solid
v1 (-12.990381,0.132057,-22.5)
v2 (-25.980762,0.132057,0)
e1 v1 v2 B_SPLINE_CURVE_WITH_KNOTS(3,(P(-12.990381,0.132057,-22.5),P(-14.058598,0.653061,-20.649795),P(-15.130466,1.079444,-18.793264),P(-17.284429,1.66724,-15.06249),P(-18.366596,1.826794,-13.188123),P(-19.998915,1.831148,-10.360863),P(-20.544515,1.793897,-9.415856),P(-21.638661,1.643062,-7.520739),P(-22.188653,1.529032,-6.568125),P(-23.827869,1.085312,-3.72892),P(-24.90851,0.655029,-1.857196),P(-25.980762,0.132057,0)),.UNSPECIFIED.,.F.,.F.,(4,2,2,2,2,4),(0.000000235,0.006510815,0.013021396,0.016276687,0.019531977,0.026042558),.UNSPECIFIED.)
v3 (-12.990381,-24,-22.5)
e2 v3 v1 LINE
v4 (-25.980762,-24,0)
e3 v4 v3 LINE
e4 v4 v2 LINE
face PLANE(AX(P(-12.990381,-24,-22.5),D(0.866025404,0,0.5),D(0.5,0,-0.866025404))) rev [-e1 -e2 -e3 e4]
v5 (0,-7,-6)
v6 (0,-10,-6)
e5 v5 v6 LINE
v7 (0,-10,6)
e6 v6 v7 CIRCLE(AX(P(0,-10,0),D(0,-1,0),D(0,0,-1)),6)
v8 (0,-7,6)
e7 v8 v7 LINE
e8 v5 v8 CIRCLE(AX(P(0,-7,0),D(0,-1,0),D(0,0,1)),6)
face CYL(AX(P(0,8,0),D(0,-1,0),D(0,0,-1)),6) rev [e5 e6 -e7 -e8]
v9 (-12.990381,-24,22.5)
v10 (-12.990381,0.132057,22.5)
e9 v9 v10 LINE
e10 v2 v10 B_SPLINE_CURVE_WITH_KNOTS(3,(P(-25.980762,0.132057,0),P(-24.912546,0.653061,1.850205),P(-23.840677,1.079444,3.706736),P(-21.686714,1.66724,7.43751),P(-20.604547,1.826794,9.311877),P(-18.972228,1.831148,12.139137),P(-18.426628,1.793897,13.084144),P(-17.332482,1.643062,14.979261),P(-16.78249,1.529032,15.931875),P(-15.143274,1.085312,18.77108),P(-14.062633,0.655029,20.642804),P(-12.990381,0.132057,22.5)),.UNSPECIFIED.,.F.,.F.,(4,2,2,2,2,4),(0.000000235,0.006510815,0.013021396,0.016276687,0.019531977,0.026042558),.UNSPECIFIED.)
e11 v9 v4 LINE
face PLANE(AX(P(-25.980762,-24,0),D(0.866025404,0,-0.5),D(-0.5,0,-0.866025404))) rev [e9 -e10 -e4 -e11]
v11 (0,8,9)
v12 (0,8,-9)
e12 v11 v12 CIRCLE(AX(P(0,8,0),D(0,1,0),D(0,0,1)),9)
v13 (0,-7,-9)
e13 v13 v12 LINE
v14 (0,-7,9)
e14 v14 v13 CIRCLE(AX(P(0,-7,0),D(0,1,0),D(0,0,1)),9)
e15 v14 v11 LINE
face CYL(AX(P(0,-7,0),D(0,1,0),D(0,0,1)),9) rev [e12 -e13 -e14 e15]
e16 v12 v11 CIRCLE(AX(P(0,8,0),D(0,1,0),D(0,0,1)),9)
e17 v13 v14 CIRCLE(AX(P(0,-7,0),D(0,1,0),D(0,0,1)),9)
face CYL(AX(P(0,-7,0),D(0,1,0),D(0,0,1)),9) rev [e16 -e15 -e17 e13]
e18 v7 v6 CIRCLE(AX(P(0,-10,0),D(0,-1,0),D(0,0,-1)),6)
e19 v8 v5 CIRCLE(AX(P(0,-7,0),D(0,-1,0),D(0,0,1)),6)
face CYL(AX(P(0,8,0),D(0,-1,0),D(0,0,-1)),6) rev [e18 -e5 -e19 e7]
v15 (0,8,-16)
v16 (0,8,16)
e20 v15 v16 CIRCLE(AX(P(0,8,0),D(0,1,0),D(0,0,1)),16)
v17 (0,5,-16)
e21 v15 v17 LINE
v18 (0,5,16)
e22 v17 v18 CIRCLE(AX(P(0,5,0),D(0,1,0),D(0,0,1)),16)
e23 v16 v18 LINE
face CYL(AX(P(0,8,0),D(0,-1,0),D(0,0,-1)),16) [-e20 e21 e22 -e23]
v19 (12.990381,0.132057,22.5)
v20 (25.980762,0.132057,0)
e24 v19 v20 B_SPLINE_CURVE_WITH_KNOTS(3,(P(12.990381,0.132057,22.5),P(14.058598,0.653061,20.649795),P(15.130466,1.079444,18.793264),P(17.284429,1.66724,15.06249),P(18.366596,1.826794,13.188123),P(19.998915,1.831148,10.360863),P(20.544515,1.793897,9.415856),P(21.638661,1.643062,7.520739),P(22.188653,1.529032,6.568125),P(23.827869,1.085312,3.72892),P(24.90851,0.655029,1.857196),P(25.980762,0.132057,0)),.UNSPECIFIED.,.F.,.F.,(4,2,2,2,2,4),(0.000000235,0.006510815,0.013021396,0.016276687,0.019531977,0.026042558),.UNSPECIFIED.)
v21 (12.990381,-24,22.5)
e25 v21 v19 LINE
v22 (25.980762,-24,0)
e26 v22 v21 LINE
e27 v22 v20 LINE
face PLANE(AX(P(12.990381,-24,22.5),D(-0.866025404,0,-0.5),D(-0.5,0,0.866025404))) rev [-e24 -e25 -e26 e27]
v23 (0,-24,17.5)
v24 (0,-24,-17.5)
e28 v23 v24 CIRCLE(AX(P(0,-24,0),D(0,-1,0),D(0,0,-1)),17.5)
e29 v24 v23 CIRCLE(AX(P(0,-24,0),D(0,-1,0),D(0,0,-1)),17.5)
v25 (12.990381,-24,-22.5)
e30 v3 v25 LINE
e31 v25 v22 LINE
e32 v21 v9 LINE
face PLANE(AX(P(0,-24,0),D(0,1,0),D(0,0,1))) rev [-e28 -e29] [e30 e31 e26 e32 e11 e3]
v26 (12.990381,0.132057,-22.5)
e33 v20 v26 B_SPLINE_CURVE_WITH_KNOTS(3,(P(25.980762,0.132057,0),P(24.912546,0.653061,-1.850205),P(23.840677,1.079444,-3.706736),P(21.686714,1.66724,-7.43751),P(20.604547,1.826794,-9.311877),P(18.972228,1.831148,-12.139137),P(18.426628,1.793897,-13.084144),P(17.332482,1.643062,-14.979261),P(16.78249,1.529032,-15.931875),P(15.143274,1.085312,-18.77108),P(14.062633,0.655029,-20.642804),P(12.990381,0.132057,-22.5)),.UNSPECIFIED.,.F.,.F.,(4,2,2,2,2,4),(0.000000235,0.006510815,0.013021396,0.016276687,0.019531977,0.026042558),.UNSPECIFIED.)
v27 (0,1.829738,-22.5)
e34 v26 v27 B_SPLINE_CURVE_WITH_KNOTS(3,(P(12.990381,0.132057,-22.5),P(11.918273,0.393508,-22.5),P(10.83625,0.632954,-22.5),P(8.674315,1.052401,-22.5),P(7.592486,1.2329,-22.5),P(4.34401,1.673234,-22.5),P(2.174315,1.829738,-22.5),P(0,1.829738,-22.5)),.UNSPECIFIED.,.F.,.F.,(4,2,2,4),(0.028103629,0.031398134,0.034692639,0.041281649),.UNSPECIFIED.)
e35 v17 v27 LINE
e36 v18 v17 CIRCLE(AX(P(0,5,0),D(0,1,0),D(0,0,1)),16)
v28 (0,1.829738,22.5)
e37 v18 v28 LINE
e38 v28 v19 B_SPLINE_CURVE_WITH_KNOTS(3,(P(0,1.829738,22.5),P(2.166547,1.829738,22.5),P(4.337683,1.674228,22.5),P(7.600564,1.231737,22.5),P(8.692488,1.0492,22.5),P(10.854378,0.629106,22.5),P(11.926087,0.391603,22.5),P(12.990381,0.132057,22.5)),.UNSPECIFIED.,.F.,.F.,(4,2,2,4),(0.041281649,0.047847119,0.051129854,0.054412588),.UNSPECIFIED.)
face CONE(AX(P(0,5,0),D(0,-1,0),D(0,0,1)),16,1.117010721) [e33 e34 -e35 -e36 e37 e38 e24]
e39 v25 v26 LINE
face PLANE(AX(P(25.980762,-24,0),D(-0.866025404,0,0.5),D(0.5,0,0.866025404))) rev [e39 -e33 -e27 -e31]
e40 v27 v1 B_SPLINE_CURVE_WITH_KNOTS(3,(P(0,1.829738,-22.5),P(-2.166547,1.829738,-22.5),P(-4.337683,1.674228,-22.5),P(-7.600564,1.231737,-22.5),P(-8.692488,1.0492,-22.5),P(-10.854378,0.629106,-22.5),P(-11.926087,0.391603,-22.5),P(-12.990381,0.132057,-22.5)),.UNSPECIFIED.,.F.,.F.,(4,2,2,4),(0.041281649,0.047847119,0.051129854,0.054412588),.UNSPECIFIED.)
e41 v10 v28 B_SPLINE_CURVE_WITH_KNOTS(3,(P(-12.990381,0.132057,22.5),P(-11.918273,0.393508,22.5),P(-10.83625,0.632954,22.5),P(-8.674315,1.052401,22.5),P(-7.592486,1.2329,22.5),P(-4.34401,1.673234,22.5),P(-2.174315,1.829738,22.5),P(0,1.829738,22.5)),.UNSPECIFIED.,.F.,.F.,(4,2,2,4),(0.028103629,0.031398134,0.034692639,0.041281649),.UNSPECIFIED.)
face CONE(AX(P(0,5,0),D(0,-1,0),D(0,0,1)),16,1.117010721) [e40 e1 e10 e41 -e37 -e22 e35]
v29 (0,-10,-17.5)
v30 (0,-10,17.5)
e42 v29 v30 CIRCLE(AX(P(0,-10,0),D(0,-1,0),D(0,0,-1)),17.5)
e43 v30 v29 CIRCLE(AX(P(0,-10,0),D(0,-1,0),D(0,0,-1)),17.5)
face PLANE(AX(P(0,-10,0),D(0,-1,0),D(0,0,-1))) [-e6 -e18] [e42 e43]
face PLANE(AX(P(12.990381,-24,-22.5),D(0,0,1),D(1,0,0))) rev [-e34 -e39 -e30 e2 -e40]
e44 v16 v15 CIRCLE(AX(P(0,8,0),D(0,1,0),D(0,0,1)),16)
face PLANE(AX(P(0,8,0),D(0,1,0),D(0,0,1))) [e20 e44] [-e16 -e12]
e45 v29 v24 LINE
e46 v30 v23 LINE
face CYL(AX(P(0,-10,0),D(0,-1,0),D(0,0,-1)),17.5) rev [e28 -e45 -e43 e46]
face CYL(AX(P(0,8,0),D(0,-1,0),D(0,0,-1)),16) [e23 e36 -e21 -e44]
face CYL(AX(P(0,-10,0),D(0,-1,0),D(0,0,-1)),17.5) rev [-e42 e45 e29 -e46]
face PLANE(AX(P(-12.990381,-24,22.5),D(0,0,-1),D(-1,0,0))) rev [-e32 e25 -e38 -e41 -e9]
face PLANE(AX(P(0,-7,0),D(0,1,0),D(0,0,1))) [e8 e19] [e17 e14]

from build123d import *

# Parameters (mm, degrees)
BOSS_EXTRUDE1_DEPTH    = 24
SKETCH_2_2_R           = 16
BOSS_EXTRUDE2_DEPTH    = 8
SKETCH_3_3_R           = 17.5
SKETCH_3_3_R_2         = 9
SKETCH_3_3_R_3         = 6
CUT_EXTRUDE1_DEPTH     = 14
BOSS_EXTRUDE3_DEPTH    = 5
SKETCH_3_4_R           = 6
CUT_EXTRUDE3_DEPTH     = 47.960089438
CUT_EXTRUDE2_START     = -32
SKETCH_3_3_2_R         = 9
CUT_EXTRUDE2_DEPTH     = 15
CUT_EXTRUDE4_START     = 5
SKETCH_2_2_2_OUTSIDE_W = 89.63
SKETCH_2_2_2_OUTSIDE_H = 82.668
SKETCH_2_2_2_OUTSIDE_R = 16
CUT_EXTRUDE4_DEPTH     = 5
CUT_EXTRUDE4_DRAFT     = -64


with BuildPart() as part:
    # Sketch 1_2 → Boss-Extrude1 (new body)
    with BuildSketch(Plane.XZ):
        Polygon((-12.990381057, 22.5), (12.990381057, 22.5), (25.980762114, 0), (12.990381057, -22.5), (-12.990381057, -22.5), (-25.980762114, 0), align=None)
    extrude(amount=BOSS_EXTRUDE1_DEPTH)

    # Sketch 2_2 → Boss-Extrude2 (add)
    with BuildSketch(Plane(origin=(0, 0, 0), x_dir=(-1, 0, 0), z_dir=(0, 1, 0))):
        with Locations(Location((0, 0, 0), (0, 0, 90))):
            Circle(SKETCH_2_2_R)
    extrude(amount=BOSS_EXTRUDE2_DEPTH)

    # Sketch 3_3 → Cut-Extrude1 (cut)
    # profile 1 of 2: a face of its own
    with BuildSketch(Plane(origin=(0, -24, 0), x_dir=(-1, 0, 0), z_dir=(0, -1, 0))):
        with Locations(Location((0, 0, 0), (0, 0, 90))):
            Circle(SKETCH_3_3_R)
        Circle(SKETCH_3_3_R_2, mode=Mode.SUBTRACT)
    # profile 2 of 2: a face of its own
    with BuildSketch(Plane(origin=(0, -24, 0), x_dir=(-1, 0, 0), z_dir=(0, -1, 0))):
        Circle(SKETCH_3_3_R_2)
        with Locations(Location((0, 0, 0), (0, 0, 90))):
            Circle(SKETCH_3_3_R_3, mode=Mode.SUBTRACT)
    extrude(amount=-CUT_EXTRUDE1_DEPTH, mode=Mode.SUBTRACT)

    # Sketch 1_2 2 → Boss-Extrude3 (add)
    with BuildSketch(Plane.XZ):
        Polygon((-12.990381057, 22.5), (12.990381057, 22.5), (25.980762114, 0), (12.990381057, -22.5), (-12.990381057, -22.5), (-25.980762114, 0), align=None)
    extrude(amount=-BOSS_EXTRUDE3_DEPTH)

    # 草图3<4> → Cut-Extrude3 (cut, through all)
    with BuildSketch(Plane(origin=(0, -24, 0), x_dir=(-1, 0, 0), z_dir=(0, -1, 0))):
        with Locations(Location((0, 0, 0), (0, 0, 90))):
            Circle(SKETCH_3_4_R)
    extrude(amount=-CUT_EXTRUDE3_DEPTH, mode=Mode.SUBTRACT)

    # Sketch 3_3 2 → Cut-Extrude2 (cut)
    with BuildSketch(Plane(origin=(0, -24, 0), x_dir=(-1, 0, 0), z_dir=(0, -1, 0)).offset(CUT_EXTRUDE2_START)):
        with Locations(Location((0, 0, 0), (0, 0, 270))):
            Circle(SKETCH_3_3_2_R)
    extrude(amount=CUT_EXTRUDE2_DEPTH, mode=Mode.SUBTRACT)


with BuildPart() as cut_extrude4_tool:
    # Sketch 2_2 2 outside → Cut-Extrude4 (with draft: the straight prism first)
    with BuildSketch(Plane(origin=(0, 0, 0), x_dir=(-1, 0, 0), z_dir=(0, 1, 0)).offset(CUT_EXTRUDE4_START)):
        Rectangle(SKETCH_2_2_2_OUTSIDE_W, SKETCH_2_2_2_OUTSIDE_H)
        with Locations(Location((0, 0, 0), (0, 0, 90))):
            Circle(SKETCH_2_2_2_OUTSIDE_R, mode=Mode.SUBTRACT)
    extrude(amount=-CUT_EXTRUDE4_DEPTH)
    # Cut-Extrude4: the draft: its side faces are tilted about the plane it starts from
    cut_extrude4_sides = [cut_extrude4_tool.faces().sort_by_distance(p)[0] for p in [
        (0, 2.5, -41.334),
        (-44.815, 2.5, 0),
        (0, 2.5, 41.334),
        (44.815, 2.5, 0),
        (0, 2.5, -16),
    ]]
    draft(cut_extrude4_sides, Plane(origin=(0, 0, 0), x_dir=(-1, 0, 0), z_dir=(0, 1, 0)).offset(CUT_EXTRUDE4_START), CUT_EXTRUDE4_DRAFT)


with BuildPart() as part_1:
    add(part.part)

    # Cut-Extrude4: cut by cut_extrude4_tool
    add(cut_extrude4_tool.part, mode=Mode.SUBTRACT)


solid = part_1.part
